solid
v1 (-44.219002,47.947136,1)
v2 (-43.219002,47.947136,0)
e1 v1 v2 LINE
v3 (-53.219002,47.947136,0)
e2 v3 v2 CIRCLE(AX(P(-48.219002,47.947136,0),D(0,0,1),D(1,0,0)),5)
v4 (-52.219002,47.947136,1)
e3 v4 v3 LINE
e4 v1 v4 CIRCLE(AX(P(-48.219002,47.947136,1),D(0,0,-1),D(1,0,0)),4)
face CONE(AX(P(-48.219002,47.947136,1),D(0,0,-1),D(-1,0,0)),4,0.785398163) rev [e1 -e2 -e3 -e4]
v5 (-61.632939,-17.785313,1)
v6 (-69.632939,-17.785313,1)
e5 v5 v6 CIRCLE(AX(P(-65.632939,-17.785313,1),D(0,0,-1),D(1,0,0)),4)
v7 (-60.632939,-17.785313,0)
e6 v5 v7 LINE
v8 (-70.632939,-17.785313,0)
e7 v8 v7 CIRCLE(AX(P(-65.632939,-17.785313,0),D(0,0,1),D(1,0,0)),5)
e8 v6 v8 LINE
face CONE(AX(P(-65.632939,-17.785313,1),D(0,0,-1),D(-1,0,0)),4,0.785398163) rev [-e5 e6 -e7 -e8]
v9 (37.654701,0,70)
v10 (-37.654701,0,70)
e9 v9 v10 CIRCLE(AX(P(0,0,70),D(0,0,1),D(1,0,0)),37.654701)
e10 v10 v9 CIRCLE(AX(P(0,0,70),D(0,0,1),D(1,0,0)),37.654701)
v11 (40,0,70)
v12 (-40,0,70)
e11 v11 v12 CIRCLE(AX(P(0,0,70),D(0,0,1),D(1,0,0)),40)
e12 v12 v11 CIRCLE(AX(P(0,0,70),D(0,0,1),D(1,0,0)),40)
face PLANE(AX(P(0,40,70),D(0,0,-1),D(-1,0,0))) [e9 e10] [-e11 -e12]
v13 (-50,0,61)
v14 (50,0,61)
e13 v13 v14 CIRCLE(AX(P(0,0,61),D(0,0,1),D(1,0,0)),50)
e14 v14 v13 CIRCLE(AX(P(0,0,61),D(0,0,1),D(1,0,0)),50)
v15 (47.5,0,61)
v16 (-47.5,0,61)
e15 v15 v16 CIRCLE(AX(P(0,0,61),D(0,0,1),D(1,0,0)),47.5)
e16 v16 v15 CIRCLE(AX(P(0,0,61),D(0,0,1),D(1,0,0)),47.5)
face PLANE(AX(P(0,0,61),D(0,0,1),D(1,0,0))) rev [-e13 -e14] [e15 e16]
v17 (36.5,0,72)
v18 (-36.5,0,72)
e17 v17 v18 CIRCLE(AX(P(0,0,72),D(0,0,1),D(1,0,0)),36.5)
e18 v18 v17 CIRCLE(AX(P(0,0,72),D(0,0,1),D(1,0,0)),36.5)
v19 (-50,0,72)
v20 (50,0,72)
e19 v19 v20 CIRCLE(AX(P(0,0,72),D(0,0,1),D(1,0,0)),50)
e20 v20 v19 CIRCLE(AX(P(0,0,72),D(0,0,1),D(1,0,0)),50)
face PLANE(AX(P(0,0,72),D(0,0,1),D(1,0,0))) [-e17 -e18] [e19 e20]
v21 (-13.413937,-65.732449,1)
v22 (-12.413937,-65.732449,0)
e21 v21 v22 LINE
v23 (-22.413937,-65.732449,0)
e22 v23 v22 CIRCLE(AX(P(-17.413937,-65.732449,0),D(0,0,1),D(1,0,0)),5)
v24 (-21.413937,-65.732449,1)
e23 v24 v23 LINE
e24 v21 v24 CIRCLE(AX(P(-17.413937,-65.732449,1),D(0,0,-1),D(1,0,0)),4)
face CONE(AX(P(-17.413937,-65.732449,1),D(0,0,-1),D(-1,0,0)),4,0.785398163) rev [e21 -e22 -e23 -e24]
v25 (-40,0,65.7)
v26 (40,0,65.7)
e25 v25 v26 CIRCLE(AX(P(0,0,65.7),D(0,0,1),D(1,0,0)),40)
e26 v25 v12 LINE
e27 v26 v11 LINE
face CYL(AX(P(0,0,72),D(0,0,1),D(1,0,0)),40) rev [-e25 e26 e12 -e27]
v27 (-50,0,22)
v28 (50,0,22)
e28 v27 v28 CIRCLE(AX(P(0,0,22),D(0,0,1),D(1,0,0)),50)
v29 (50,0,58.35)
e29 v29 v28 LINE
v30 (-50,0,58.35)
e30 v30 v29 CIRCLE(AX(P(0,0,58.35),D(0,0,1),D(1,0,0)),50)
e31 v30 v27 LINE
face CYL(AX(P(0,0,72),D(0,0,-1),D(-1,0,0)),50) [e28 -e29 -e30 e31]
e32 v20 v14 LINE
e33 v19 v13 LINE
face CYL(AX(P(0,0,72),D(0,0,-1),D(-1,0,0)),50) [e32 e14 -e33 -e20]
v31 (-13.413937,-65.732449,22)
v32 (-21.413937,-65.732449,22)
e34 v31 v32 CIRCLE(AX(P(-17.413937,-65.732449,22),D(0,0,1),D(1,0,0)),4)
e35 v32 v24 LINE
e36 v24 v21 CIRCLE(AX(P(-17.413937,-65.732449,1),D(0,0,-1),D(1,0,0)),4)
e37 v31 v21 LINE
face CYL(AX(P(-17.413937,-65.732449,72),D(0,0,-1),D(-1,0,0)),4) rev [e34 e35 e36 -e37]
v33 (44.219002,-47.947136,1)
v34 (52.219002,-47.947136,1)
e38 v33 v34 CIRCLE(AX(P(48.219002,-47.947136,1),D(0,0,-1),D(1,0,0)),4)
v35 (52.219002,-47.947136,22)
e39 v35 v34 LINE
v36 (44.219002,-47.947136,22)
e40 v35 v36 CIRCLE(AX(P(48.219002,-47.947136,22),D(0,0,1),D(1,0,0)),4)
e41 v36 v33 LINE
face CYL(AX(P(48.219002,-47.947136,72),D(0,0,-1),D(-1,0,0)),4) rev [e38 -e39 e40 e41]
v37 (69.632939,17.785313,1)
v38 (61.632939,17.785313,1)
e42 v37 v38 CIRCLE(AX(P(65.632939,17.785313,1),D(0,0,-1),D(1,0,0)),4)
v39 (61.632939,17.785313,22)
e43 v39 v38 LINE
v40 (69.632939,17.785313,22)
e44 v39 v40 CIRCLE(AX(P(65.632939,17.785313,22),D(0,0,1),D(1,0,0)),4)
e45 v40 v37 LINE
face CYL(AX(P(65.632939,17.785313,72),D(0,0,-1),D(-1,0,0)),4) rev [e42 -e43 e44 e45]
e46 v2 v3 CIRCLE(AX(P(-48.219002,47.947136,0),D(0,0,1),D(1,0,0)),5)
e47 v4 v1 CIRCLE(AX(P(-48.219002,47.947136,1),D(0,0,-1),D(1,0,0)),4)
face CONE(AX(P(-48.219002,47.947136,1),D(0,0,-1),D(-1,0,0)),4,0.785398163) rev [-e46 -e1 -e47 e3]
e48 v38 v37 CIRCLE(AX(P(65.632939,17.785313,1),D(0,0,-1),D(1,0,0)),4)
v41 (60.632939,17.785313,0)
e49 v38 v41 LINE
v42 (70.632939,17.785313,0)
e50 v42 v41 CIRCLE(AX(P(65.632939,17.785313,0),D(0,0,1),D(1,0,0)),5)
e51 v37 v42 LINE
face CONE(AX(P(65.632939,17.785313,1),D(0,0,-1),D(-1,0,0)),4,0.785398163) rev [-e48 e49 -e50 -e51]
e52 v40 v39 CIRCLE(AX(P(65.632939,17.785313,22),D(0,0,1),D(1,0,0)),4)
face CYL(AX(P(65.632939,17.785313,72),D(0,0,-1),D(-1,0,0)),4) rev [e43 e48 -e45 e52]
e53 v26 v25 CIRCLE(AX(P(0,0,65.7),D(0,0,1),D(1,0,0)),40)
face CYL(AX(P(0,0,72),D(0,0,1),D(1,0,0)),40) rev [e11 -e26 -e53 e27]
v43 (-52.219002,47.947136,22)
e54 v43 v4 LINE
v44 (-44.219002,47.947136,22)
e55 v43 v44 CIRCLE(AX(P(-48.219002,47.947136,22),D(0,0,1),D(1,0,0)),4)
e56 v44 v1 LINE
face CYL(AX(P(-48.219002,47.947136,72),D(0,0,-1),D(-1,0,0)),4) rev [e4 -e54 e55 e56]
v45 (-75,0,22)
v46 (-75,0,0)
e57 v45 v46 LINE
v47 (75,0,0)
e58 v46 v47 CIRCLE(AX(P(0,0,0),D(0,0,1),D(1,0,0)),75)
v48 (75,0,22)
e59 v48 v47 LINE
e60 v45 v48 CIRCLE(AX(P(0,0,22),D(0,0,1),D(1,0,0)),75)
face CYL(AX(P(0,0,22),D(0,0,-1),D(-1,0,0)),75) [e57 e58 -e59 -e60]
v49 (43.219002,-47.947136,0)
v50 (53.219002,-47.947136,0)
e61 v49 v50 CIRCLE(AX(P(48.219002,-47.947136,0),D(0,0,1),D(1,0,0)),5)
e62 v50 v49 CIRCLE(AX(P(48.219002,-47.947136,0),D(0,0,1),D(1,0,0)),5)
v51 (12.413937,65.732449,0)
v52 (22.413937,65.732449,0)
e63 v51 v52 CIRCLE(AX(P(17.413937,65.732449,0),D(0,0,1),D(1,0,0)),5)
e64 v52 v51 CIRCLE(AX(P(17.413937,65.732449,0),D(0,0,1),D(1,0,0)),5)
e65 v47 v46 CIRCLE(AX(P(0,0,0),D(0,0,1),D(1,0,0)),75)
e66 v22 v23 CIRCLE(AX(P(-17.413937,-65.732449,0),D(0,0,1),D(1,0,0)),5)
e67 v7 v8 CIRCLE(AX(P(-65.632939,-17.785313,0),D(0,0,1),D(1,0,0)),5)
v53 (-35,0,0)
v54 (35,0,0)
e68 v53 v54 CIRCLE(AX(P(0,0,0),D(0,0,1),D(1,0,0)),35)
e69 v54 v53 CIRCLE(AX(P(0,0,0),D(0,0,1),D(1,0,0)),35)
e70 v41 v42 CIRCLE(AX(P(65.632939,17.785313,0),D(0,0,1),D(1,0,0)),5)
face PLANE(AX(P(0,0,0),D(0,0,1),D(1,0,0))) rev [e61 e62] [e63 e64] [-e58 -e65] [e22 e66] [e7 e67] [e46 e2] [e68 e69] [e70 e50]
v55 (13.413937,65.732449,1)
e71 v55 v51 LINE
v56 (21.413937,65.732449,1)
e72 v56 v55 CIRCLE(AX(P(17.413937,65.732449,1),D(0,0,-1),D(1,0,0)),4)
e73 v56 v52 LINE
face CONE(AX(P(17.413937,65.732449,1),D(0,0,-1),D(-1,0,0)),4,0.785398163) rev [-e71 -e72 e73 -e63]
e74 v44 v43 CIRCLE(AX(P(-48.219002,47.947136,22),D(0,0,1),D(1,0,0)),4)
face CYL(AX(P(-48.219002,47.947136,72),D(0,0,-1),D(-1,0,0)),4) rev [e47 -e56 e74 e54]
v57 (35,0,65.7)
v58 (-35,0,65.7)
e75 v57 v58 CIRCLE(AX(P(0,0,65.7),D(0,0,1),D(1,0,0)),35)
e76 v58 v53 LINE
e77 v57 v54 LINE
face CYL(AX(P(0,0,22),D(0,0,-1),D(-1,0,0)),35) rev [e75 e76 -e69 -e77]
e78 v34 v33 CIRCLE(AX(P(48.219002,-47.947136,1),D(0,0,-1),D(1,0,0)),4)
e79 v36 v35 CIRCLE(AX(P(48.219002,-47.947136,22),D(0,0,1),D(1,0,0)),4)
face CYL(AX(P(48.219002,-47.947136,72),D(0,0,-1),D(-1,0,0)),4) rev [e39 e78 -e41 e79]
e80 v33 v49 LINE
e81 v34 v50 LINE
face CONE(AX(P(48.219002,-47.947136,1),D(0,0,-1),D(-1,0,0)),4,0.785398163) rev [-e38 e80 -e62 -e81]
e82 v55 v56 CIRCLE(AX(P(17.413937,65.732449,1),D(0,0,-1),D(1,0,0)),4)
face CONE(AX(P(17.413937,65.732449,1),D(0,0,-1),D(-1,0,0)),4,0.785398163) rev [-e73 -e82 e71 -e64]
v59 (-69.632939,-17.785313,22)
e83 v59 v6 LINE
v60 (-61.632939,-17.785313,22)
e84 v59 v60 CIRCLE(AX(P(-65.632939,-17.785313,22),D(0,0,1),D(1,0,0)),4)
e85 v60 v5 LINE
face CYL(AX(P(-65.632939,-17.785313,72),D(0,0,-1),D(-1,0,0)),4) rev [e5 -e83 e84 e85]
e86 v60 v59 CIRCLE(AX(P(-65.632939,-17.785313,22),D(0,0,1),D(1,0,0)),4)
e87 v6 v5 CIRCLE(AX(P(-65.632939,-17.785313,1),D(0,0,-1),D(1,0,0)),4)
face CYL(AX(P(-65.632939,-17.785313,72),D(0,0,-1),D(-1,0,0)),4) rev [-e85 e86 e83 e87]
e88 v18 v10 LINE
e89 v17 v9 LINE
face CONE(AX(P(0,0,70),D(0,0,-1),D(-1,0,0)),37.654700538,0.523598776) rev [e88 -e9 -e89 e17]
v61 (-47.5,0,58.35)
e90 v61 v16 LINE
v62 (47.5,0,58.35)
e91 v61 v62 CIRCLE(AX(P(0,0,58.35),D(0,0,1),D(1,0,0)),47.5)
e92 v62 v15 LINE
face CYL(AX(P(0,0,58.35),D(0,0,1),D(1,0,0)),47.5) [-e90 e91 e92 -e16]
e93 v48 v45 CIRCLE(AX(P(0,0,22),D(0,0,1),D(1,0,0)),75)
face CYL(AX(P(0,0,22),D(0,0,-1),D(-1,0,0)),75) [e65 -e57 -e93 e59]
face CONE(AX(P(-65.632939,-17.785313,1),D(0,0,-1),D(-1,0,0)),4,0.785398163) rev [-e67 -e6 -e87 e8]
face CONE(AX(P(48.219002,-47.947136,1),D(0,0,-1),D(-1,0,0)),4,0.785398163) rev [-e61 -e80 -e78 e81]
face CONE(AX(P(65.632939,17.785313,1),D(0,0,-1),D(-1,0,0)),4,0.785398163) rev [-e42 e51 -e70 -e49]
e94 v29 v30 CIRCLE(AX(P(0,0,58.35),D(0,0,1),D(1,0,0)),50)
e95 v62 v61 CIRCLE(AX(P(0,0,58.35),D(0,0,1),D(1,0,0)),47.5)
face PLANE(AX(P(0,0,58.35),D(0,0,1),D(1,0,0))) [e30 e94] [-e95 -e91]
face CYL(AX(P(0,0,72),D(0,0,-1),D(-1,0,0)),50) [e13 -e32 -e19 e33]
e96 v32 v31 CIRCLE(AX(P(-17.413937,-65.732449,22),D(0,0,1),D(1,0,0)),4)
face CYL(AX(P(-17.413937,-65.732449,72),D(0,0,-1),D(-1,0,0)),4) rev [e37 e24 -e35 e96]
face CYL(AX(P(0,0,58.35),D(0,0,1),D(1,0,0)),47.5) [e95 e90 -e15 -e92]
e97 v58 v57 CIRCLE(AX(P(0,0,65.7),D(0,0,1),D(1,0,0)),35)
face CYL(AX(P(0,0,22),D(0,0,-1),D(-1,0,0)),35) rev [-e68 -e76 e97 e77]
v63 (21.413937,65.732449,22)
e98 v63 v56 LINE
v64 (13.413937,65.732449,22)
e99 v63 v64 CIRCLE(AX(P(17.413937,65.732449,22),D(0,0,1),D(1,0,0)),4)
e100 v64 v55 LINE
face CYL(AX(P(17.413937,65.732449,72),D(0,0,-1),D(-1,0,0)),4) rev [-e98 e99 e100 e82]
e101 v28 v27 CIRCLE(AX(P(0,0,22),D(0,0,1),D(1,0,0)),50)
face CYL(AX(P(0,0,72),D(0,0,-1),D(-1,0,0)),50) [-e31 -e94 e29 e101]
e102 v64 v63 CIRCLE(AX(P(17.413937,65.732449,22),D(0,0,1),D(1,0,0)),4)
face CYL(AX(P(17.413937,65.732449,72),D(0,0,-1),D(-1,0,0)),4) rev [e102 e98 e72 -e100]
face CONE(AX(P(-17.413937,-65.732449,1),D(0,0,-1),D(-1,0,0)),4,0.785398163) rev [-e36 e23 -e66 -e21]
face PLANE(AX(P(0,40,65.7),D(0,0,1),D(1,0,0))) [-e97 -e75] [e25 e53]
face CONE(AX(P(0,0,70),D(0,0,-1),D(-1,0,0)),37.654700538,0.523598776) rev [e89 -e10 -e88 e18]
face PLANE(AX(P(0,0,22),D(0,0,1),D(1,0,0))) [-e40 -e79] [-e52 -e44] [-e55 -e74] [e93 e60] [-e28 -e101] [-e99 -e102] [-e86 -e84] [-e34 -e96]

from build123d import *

# Parameters (mm, degrees)
SKETCH1_R           = 75
SKETCH1_R_2         = 35
BOSS_EXTRUDE1_DEPTH = 22
BOSS_EXTRUDE2_START = 22
SKETCH2_R           = 50
SKETCH2_R_2         = 35
BOSS_EXTRUDE2_DEPTH = 50
CUT_EXTRUDE1_START  = 58.35
SKETCH3_R           = 50
SKETCH3_R_2         = 47.5
CUT_EXTRUDE1_DEPTH  = 2.65
SKETCH5_R           = 4
CUT_EXTRUDE2_DEPTH  = 129.195163715
CHAMFER1_SIZE       = 1


with BuildPart() as part:
    # Sketch1 → Boss-Extrude1 (new body)
    with BuildSketch(Plane.XY):
        Circle(SKETCH1_R)
        Circle(SKETCH1_R_2, mode=Mode.SUBTRACT)
    extrude(amount=BOSS_EXTRUDE1_DEPTH)

    # Sketch2 → Boss-Extrude2 (add)
    with BuildSketch(Plane.XY.offset(BOSS_EXTRUDE2_START)):
        Circle(SKETCH2_R)
        Circle(SKETCH2_R_2, mode=Mode.SUBTRACT)
    extrude(amount=BOSS_EXTRUDE2_DEPTH)

    # Sketch3 → Cut-Extrude1 (cut)
    with BuildSketch(Plane.XY.offset(CUT_EXTRUDE1_START)):
        Circle(SKETCH3_R)
        Circle(SKETCH3_R_2, mode=Mode.SUBTRACT)
    extrude(amount=CUT_EXTRUDE1_DEPTH, mode=Mode.SUBTRACT)

    # Sketch5 → Cut-Extrude2 (cut, through all)
    with BuildSketch(Plane(origin=(0, 0, 0), x_dir=(-1, 0, 0), z_dir=(0, 0, -1))):
        with Locations((-17.413936667, 65.732448682)):
            Circle(SKETCH5_R)
        with Locations((48.219002079, 47.947135874)):
            Circle(SKETCH5_R)
        with Locations((65.632938745, -17.785312808)):
            Circle(SKETCH5_R)
        with Locations((17.413936667, -65.732448682)):
            Circle(SKETCH5_R)
        with Locations((-48.219002079, -47.947135874)):
            Circle(SKETCH5_R)
        with Locations((-65.632938745, 17.785312808)):
            Circle(SKETCH5_R)
    extrude(amount=-CUT_EXTRUDE2_DEPTH, mode=Mode.SUBTRACT)

    # Chamfer1
    chamfer1_edges = [part.edges().sort_by_distance(p)[0] for p in [
        (21.413936667, 65.732448682, 0),
        (-44.219002079, 47.947135874, 0),
        (-61.632938745, -17.785312808, 0),
        (-13.413936667, -65.732448682, 0),
        (52.219002079, -47.947135874, 0),
        (69.632938745, 17.785312808, 0),
    ]]
    chamfer(chamfer1_edges, length=CHAMFER1_SIZE)

    # Sketch7 → Cut-Revolve1 (revolve, cut)
    with BuildSketch(Plane(origin=(0, 0, 0), x_dir=(0, 0, -1), z_dir=(1, 0, 0)), mode=Mode.PRIVATE) as cut_revolve1_sk:
        Polygon((-72, 35), (-72, 36.5), (-70, 37.654700538), (-70, 40), (-65.7, 40), (-65.7, 35), align=None)
    revolve(cut_revolve1_sk.sketch.rotate(Axis((0, 0, 72), (0, 0, -1)), 90), axis=Axis((0, 0, 72), (0, 0, -1)), mode=Mode.SUBTRACT)


solid = part.part
